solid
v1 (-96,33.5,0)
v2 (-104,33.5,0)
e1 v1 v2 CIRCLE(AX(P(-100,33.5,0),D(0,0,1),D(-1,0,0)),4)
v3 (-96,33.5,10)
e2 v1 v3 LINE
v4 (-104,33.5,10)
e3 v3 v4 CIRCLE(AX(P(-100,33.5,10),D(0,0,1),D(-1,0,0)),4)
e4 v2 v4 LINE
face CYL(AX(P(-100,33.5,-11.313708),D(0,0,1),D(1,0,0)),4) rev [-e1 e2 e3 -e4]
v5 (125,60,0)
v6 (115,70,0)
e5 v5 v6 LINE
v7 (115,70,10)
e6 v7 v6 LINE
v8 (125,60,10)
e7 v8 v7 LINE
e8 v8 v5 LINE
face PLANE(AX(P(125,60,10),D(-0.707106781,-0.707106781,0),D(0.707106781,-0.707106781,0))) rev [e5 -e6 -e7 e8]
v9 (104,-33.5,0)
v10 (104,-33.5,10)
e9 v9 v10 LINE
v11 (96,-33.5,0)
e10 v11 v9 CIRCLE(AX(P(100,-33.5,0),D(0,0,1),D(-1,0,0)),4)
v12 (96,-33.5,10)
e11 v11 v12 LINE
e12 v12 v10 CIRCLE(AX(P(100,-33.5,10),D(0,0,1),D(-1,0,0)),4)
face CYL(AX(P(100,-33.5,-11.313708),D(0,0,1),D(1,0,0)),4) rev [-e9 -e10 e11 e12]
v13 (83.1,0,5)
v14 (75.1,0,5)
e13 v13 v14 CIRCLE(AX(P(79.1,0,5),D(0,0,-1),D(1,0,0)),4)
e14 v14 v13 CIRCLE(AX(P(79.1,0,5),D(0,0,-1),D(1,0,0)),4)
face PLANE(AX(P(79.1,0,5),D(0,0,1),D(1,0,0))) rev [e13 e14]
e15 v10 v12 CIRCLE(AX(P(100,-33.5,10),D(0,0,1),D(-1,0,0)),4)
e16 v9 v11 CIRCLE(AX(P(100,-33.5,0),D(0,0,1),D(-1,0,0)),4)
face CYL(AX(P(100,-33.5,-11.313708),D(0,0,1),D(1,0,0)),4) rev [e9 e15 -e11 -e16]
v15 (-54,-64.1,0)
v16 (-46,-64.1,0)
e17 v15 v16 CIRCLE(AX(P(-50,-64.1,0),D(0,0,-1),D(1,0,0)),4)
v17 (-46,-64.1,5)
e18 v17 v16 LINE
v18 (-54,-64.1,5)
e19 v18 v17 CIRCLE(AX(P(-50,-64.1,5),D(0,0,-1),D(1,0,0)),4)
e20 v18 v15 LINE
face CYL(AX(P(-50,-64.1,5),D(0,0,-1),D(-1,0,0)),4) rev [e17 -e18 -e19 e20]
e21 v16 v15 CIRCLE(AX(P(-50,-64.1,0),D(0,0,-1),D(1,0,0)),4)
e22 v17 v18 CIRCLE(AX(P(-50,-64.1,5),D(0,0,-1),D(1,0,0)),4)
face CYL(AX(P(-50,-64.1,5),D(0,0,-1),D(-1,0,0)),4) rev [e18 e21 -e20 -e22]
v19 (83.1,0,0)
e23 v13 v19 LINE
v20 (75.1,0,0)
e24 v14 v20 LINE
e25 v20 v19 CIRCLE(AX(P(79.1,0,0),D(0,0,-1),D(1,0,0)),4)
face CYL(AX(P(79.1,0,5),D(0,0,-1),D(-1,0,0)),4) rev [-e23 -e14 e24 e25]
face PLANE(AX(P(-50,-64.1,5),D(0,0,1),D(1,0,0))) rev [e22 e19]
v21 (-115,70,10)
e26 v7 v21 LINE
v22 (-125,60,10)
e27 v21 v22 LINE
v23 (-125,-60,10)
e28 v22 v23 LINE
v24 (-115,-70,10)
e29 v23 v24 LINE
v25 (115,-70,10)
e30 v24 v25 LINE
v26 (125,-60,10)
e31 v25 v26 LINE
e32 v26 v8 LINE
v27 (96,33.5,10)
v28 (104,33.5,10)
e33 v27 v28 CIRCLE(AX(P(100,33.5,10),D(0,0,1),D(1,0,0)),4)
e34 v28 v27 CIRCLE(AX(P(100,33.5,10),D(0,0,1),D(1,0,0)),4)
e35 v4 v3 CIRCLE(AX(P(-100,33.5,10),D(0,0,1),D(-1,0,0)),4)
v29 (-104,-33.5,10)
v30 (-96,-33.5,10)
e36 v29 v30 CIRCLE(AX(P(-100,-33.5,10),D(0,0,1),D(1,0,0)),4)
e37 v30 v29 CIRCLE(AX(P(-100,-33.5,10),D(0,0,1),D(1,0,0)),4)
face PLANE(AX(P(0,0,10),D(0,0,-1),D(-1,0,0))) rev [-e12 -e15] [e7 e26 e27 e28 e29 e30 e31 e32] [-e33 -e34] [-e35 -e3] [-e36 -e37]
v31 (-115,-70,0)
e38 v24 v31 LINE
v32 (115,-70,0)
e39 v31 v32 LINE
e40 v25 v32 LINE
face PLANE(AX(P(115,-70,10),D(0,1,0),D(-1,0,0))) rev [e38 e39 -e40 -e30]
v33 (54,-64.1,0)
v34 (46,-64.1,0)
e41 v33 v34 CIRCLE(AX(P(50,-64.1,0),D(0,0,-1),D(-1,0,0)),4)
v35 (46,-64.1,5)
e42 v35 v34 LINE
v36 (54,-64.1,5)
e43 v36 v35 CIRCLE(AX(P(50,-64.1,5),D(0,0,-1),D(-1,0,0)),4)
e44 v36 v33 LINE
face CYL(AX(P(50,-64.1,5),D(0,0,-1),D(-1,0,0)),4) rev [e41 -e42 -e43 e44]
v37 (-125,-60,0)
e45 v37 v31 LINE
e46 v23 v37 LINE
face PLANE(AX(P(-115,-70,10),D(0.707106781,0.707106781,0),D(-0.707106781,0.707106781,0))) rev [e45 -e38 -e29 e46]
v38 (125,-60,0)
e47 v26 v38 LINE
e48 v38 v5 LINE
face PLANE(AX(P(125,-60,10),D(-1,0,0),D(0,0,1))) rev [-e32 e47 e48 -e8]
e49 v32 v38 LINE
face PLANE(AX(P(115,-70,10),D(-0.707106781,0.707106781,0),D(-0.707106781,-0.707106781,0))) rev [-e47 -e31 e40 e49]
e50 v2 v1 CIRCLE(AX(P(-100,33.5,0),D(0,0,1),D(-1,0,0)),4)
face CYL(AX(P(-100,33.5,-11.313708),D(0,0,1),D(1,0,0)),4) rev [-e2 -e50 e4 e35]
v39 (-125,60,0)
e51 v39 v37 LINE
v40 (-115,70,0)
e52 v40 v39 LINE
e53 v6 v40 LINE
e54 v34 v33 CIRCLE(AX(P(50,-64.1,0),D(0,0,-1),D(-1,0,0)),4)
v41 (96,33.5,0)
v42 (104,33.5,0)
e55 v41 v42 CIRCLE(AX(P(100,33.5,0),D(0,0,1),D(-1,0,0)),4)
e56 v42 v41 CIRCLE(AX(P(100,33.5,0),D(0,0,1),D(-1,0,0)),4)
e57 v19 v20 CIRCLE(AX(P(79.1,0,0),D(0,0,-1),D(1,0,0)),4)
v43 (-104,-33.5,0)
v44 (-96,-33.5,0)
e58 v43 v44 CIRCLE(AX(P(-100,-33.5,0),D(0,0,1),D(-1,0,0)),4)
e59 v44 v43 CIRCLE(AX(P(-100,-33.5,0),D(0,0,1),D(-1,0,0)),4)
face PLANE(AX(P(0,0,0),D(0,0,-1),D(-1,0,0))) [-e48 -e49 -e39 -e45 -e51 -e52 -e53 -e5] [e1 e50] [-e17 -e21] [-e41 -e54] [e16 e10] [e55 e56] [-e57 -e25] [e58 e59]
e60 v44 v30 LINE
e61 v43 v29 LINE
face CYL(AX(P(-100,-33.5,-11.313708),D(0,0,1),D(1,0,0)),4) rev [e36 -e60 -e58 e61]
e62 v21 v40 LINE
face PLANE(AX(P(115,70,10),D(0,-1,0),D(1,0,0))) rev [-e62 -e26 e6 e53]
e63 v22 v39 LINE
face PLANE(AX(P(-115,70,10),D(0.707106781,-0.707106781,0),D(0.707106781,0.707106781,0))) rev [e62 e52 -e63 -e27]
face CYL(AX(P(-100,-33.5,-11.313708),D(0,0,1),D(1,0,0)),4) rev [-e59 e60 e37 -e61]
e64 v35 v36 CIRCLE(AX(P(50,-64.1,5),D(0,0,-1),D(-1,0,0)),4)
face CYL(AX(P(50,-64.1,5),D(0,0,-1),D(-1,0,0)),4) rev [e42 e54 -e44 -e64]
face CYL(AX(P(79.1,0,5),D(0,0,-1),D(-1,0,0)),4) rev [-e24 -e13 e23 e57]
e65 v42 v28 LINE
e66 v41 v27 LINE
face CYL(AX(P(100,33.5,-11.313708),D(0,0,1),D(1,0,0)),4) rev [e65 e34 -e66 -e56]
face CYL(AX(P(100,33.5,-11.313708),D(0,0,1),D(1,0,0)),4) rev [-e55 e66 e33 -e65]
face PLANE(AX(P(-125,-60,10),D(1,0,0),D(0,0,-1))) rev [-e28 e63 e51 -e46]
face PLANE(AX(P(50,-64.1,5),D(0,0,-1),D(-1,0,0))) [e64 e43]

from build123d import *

# Parameters (mm, degrees)
BOSS_EXTRUDE1_DEPTH = 10
SKETCH6_R           = 4
CUT_EXTRUDE3_DEPTH  = 5
BOSS_EXTRUDE3_START = 5
SKETCH7_R           = 4
BOSS_EXTRUDE3_DEPTH = 5
SKETCH8_R           = 4
CUT_EXTRUDE4_DEPTH  = 5
SKETCH11_R          = 4
CUT_EXTRUDE5_DEPTH  = 10


with BuildPart() as part:
    # Sketch1 → Boss-Extrude1 (new body)
    with BuildSketch(Plane.XY):
        Polygon((-115, 70), (-125, 60), (-125, -60), (-115, -70), (115, -70), (125, -60), (125, 60), (115, 70), align=None)
    extrude(amount=BOSS_EXTRUDE1_DEPTH)

    # Sketch6 → Cut-Extrude3 (cut)
    with BuildSketch(Plane(origin=(0, 0, 0), x_dir=(-1, 0, 0), z_dir=(0, 0, -1))):
        with Locations((79.1, 0)):
            Circle(SKETCH6_R)
        with Locations(Location((-79.1, 0, 0), (0, 0, 180))):
            Circle(SKETCH6_R)
    extrude(amount=-CUT_EXTRUDE3_DEPTH, mode=Mode.SUBTRACT)

    # Sketch7 → Boss-Extrude3 (add)
    with BuildSketch(Plane(origin=(0, 0, 5), x_dir=(-1, 0, 0), z_dir=(0, 0, -1)).offset(BOSS_EXTRUDE3_START)):
        with Locations((79.1, 0)):
            Circle(SKETCH7_R)
    extrude(amount=-BOSS_EXTRUDE3_DEPTH)

    # Sketch8 → Cut-Extrude4 (cut)
    with BuildSketch(Plane(origin=(0, 0, 0), x_dir=(-1, 0, 0), z_dir=(0, 0, -1))):
        with Locations((-50, -64.1)):
            Circle(SKETCH8_R)
        with Locations(Location((50, -64.1, 0), (0, 0, 180))):
            Circle(SKETCH8_R)
    extrude(amount=-CUT_EXTRUDE4_DEPTH, mode=Mode.SUBTRACT)

    # Sketch11 → Cut-Extrude5 (cut)
    with BuildSketch(Plane.XY.offset(10)):
        with Locations((100, 33.5)):
            Circle(SKETCH11_R)
        with Locations(Location((-100, 33.5, 0), (0, 0, 180))):
            Circle(SKETCH11_R)
        with Locations((-100, -33.5)):
            Circle(SKETCH11_R)
        with Locations(Location((100, -33.5, 0), (0, 0, 180))):
            Circle(SKETCH11_R)
    extrude(amount=-CUT_EXTRUDE5_DEPTH, mode=Mode.SUBTRACT)


solid = part.part
